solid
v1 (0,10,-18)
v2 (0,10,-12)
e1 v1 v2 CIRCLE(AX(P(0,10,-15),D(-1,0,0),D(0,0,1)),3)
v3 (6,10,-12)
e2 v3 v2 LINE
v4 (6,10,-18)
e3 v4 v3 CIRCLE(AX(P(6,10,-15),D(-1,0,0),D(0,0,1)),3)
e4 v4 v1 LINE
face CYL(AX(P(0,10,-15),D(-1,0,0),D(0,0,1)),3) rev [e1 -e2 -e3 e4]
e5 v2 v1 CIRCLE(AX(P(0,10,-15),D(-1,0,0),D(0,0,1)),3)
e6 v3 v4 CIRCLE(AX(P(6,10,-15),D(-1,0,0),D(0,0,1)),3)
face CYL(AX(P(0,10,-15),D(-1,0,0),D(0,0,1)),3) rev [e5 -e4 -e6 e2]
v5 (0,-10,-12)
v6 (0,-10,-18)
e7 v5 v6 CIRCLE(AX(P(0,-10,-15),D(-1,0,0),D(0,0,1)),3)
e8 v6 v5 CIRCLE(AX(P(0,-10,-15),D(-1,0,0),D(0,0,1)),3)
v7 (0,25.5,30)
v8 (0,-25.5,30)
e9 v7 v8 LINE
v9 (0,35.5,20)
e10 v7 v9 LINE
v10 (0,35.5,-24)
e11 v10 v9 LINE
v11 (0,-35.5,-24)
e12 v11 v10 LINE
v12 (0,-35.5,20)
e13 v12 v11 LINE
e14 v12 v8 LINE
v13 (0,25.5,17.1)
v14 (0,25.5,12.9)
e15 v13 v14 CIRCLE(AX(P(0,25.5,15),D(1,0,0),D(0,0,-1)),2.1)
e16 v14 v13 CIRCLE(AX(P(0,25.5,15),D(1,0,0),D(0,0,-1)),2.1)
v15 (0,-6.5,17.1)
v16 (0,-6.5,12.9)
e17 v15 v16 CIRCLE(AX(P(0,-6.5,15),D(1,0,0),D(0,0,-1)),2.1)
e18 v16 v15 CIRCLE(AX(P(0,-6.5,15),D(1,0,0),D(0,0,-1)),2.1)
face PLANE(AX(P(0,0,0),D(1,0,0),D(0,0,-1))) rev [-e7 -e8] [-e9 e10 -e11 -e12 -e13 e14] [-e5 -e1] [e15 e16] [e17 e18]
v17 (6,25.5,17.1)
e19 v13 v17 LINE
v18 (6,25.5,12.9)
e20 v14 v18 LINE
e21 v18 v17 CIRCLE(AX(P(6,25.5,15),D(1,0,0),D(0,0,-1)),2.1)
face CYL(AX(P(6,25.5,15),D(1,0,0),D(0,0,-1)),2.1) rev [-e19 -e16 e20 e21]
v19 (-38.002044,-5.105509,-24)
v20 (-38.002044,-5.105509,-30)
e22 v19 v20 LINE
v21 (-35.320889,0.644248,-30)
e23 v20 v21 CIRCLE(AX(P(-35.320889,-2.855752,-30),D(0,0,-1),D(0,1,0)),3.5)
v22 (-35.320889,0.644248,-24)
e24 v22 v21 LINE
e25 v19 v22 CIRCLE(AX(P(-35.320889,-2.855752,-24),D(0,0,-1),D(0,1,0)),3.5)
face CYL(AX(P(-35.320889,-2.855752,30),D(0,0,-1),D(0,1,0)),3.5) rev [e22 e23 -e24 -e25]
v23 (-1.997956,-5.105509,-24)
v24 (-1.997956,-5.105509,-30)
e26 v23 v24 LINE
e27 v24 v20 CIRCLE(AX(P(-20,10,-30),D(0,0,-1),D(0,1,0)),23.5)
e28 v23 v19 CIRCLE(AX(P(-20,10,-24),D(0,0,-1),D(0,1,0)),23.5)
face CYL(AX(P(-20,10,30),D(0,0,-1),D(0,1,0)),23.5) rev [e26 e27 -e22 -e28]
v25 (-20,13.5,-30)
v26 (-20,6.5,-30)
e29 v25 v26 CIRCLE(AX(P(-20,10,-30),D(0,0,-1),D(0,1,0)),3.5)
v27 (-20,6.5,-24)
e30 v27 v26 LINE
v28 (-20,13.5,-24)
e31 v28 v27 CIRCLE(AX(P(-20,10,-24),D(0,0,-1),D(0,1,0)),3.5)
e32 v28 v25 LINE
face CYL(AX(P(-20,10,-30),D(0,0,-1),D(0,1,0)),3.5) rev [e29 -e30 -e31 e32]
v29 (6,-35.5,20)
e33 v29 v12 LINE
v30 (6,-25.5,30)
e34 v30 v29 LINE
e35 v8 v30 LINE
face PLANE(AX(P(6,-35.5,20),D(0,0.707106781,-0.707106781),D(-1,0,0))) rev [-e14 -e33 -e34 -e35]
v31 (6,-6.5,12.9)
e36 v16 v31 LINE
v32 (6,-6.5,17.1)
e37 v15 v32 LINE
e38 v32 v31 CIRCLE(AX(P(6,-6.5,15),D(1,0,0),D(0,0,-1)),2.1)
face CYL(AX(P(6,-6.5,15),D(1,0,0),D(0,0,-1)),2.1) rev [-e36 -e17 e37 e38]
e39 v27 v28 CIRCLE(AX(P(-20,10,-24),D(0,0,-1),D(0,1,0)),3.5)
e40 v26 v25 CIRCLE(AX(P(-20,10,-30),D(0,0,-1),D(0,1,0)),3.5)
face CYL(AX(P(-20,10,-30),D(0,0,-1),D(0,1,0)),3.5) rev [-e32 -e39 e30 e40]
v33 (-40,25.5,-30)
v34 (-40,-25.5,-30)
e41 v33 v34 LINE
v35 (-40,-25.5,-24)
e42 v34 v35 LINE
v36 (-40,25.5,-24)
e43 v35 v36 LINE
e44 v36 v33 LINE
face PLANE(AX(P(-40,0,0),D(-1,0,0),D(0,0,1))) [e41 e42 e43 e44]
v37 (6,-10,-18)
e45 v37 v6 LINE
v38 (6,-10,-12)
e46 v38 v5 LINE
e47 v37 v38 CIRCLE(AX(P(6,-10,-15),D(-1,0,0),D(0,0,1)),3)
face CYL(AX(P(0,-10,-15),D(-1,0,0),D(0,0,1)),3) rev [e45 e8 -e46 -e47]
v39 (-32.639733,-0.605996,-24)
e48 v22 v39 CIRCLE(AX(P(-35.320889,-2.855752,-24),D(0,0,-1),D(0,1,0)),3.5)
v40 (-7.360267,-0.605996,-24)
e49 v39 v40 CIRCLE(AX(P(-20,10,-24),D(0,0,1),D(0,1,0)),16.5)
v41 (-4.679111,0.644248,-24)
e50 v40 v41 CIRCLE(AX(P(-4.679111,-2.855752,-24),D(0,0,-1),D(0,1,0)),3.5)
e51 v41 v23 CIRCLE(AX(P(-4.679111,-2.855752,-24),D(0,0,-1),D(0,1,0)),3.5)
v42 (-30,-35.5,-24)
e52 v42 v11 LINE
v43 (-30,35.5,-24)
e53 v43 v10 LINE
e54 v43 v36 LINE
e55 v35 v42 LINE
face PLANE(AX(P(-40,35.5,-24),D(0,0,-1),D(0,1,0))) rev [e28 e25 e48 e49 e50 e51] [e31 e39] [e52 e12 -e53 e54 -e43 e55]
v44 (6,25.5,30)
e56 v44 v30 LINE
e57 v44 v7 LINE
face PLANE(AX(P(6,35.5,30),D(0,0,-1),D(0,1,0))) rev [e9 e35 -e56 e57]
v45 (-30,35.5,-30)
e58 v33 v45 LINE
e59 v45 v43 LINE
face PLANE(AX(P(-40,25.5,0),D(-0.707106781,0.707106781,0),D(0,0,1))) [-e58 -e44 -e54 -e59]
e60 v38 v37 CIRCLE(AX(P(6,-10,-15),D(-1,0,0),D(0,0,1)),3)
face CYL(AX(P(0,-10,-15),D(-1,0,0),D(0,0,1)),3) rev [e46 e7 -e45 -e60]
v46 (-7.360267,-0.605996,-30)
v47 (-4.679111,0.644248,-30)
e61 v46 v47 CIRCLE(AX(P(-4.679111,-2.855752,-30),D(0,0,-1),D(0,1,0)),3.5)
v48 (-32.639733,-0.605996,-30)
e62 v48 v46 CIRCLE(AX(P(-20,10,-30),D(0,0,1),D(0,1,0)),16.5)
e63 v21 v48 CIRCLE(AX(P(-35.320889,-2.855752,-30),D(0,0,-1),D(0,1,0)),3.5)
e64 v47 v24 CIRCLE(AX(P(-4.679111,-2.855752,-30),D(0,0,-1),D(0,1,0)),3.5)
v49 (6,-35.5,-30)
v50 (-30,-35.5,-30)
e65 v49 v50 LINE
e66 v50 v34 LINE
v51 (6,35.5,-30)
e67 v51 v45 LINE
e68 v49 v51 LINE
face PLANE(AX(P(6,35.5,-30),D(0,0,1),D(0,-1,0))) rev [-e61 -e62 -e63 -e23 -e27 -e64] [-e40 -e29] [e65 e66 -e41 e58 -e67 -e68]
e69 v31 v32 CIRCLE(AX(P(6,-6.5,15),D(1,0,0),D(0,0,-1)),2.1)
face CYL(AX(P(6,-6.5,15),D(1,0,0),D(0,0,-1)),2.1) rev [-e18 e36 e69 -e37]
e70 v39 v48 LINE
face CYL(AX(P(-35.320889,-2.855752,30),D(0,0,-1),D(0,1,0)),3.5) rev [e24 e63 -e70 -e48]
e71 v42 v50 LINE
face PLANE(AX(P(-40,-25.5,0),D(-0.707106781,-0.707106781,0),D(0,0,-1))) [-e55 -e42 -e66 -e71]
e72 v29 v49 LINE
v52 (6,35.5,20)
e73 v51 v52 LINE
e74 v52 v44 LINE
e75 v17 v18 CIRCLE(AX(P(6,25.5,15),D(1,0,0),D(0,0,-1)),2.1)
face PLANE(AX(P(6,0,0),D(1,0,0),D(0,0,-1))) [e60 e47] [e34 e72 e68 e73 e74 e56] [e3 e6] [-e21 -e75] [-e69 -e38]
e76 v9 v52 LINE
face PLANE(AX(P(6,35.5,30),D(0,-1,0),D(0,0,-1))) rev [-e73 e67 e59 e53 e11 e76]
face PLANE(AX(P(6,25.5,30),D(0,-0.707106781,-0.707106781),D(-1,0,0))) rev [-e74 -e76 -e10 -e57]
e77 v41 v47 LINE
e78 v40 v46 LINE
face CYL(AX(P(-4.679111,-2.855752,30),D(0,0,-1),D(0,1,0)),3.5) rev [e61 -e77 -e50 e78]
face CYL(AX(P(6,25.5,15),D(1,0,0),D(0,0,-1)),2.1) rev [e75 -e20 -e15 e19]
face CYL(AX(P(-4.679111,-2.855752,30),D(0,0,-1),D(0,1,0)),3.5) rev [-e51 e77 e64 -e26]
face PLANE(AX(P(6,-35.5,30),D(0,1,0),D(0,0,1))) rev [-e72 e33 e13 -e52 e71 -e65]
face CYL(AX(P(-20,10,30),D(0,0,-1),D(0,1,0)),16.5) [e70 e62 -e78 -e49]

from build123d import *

# Parameters (mm, degrees)
SKETCH_1_W                = 60
SKETCH_1_H                = 71
EXTRUDE_1_DEPTH           = 6
HOLE_WIZARD_M5_1_D        = 4.2
HOLE_WIZARD_6_0_6_1_D     = 6
SKETCH_7_W                = 6
SKETCH_7_H                = 71
EXTRUDE_2_DEPTH           = 40
HOLE_WIZARD_7_0_7_1_D     = 7
HOLE_WIZARD_7_0_7_1_DEPTH = 15
HOLE_WIZARD_7_0_7_1_TIP   = 2.103012167
CUT_EXTRUDE_1_DEPTH       = 81.375680401
CHAMFER_1_SIZE            = 10


with BuildPart() as part:
    # 草图1 → 凸台-拉伸1 (new body)
    with BuildSketch(Plane(origin=(0, 0, 0), x_dir=(0, 0, -1), z_dir=(1, 0, 0))):
        Rectangle(SKETCH_1_W, SKETCH_1_H)
    extrude(amount=EXTRUDE_1_DEPTH)

    # M5 螺纹孔1 (through all)
    with Locations(Plane(origin=(6, 0, 0), x_dir=(0, 0, -1), z_dir=(1, 0, 0))):
        with Locations((-15, 25.5), (-15, -6.5)):
            Hole(HOLE_WIZARD_M5_1_D / 2)

    # Ø6.0 (6) 直径孔1 (through all)
    with Locations(Plane.ZY):
        with Locations((-15, 10), (-15, -10)):
            Hole(HOLE_WIZARD_6_0_6_1_D / 2)

    # 草图7 → 凸台-拉伸2 (add)
    with BuildSketch(Plane.ZY):
        with Locations((-27, 0)):
            Rectangle(SKETCH_7_W, SKETCH_7_H)
    extrude(amount=EXTRUDE_2_DEPTH)

    # Ø7.0 (7) 直径孔1
    with Locations(Plane(origin=(0, 0, -30), x_dir=(-1, 0, 0), z_dir=(0, 0, -1))):
        with Locations((20, 10)):
            Hole(HOLE_WIZARD_7_0_7_1_D / 2, depth=HOLE_WIZARD_7_0_7_1_DEPTH)
            with Locations((0, 0, -(HOLE_WIZARD_7_0_7_1_DEPTH + HOLE_WIZARD_7_0_7_1_TIP / 2))):  # 118° drill point
                Cone(0, HOLE_WIZARD_7_0_7_1_D / 2, HOLE_WIZARD_7_0_7_1_TIP, mode=Mode.SUBTRACT)

    # 草图10 → 切除-拉伸1 (cut, through all)
    with BuildSketch(Plane(origin=(0, 0, -30), x_dir=(-1, 0, 0), z_dir=(0, 0, -1))):
        with BuildLine():
            ThreePointArc((1.997955587, -5.105508828), (20, -13.5), (38.002044413, -5.105508828))
            ThreePointArc((38.002044413, -5.105508828), (37.570645496, -0.174596643), (32.639733311, -0.60599556))
            ThreePointArc((32.639733311, -0.60599556), (20, -6.5), (7.360266689, -0.60599556))
            ThreePointArc((7.360266689, -0.60599556), (2.429354504, -0.174596643), (1.997955587, -5.105508828))
        make_face()
    extrude(amount=-CUT_EXTRUDE_1_DEPTH, mode=Mode.SUBTRACT)

    # 倒角1
    chamfer_1_edges = [part.edges().sort_by_distance(p)[0] for p in [
        (-40, -35.5, -27),
        (-40, 35.5, -27),
        (3, -35.5, 30),
        (3, 35.5, 30),
    ]]
    chamfer(chamfer_1_edges, length=CHAMFER_1_SIZE)


solid = part.part
